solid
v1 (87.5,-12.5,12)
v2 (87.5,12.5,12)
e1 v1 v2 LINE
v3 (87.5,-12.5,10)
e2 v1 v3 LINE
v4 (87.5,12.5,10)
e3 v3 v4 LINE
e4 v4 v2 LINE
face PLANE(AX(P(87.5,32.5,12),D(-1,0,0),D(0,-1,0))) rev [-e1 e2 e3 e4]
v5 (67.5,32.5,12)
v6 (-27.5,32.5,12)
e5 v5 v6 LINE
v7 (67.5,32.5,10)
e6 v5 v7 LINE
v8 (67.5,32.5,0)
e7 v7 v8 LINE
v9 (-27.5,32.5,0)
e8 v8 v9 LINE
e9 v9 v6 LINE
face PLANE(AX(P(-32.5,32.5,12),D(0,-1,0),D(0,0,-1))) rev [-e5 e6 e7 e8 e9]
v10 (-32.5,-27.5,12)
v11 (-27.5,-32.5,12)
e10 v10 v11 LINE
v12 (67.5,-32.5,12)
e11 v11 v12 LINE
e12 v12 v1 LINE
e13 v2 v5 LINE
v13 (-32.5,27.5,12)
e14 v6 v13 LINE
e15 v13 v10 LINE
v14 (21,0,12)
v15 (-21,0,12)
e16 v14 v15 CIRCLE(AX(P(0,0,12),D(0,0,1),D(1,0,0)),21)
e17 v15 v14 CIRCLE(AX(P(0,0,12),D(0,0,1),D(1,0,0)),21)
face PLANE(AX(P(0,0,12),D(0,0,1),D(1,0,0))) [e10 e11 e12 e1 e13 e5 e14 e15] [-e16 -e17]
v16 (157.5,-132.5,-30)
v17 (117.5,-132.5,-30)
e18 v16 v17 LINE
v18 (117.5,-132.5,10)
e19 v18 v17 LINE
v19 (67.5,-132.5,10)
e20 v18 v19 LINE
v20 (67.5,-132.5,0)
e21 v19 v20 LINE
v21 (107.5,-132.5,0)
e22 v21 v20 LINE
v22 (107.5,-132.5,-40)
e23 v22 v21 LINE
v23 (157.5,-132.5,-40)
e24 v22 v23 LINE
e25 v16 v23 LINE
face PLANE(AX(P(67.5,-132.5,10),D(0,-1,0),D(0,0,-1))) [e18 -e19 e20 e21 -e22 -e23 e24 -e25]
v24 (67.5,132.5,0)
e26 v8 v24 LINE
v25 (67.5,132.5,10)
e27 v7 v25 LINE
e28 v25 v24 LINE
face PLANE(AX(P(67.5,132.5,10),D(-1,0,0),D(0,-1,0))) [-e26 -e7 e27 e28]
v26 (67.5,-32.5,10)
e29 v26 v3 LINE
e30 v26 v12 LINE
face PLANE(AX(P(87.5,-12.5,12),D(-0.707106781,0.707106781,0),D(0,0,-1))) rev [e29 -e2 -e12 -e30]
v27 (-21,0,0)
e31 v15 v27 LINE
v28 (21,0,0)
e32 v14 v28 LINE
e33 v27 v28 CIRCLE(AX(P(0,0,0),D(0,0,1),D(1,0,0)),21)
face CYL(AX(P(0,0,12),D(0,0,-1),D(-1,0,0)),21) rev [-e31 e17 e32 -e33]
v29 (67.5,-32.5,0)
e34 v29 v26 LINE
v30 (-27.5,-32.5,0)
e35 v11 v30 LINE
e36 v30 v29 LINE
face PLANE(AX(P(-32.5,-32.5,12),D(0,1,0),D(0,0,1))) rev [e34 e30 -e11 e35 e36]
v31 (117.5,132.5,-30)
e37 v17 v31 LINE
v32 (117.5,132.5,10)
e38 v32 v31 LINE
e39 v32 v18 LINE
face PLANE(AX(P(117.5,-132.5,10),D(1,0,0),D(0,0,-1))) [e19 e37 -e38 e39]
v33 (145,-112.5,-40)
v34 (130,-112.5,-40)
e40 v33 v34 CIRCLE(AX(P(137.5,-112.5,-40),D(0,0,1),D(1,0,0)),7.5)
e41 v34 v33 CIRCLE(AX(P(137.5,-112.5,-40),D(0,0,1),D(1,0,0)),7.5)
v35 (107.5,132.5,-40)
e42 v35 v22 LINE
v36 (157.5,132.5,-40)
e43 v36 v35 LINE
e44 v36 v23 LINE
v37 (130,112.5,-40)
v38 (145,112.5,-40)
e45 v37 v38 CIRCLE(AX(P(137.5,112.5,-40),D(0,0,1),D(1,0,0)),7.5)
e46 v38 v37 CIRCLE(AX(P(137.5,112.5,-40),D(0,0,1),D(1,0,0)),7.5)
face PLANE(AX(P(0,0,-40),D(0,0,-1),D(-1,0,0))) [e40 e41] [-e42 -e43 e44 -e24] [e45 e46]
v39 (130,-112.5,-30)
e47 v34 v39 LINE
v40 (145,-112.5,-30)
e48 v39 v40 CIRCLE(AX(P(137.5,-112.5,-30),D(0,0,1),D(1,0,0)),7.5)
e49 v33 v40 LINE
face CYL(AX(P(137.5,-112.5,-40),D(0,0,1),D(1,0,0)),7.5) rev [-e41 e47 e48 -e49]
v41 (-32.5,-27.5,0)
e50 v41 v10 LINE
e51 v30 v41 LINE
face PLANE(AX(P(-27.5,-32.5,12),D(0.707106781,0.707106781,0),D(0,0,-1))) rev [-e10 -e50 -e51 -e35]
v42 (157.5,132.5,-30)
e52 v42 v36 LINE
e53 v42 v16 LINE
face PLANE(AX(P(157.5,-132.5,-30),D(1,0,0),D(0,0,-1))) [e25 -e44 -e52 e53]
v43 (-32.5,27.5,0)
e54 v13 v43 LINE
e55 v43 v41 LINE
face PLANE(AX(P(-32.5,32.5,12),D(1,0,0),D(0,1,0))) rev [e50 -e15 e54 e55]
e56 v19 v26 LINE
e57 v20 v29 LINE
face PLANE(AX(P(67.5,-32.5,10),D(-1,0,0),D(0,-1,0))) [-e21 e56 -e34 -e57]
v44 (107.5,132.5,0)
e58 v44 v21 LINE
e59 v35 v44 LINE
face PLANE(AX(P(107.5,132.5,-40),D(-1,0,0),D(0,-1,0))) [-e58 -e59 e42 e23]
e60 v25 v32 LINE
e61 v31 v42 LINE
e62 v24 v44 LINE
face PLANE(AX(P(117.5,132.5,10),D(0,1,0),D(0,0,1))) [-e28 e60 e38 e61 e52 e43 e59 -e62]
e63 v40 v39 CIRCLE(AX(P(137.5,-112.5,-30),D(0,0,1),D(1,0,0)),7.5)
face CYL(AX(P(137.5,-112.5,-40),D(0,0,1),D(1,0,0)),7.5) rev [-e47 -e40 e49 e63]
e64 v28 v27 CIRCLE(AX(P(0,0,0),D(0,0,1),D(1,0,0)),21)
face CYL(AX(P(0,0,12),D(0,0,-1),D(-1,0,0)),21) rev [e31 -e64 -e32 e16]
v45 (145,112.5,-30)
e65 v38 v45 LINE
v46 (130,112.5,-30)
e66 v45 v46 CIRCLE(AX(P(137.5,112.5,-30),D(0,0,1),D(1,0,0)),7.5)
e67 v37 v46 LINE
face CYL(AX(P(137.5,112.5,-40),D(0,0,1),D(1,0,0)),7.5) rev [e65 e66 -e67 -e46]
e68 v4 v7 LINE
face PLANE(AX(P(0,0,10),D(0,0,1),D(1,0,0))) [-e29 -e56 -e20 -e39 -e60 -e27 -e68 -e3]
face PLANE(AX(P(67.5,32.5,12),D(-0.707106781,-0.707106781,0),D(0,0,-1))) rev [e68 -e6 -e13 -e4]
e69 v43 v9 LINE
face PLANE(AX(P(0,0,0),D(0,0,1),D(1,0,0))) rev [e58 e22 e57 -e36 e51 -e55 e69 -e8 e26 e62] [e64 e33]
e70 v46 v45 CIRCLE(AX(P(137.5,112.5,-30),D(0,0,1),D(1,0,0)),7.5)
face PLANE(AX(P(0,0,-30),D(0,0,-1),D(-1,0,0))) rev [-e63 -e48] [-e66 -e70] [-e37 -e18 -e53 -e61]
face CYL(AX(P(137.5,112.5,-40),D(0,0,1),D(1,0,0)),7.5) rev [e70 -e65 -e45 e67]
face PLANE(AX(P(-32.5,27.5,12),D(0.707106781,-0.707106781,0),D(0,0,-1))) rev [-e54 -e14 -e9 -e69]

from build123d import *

# Parameters (mm, degrees)
SKETCH_1_R          = 21
EXTRUDE_1_DEPTH     = 12
CHAMFER_1_SIZE      = 5
CHAMFER_2_SIZE      = 20
EXTRUDE_2_DEPTH     = 10
SKETCH_4_W          = 10
SKETCH_4_H          = 265
EXTRUDE_3_DEPTH     = 50
SKETCH_6_W          = 50
SKETCH_6_H          = 265
EXTRUDE_4_DEPTH     = 10
SKETCH_7_R          = 7.5
CUT_EXTRUDE_1_DEPTH = 211.063085762


with BuildPart() as part:
    # 草图1 → 凸台-拉伸1 (new body)
    with BuildSketch(Plane.XY):
        Polygon((32.5, 32.5), (87.5, 32.5), (87.5, -32.5), (32.5, -32.5), (-32.5, -32.5), (-32.5, 32.5), align=None)
        Circle(SKETCH_1_R, mode=Mode.SUBTRACT)
    extrude(amount=EXTRUDE_1_DEPTH)

    # 倒角1
    chamfer_1_edges = [part.edges().sort_by_distance(p)[0] for p in [
        (-32.5, -32.5, 6),
        (-32.5, 32.5, 6),
    ]]
    chamfer(chamfer_1_edges, length=CHAMFER_1_SIZE)

    # 倒角2
    chamfer_2_edges = [part.edges().sort_by_distance(p)[0] for p in [
        (87.5, 32.5, 6),
        (87.5, -32.5, 6),
    ]]
    chamfer(chamfer_2_edges, length=CHAMFER_2_SIZE)

    # 草图3 → 凸台-拉伸2 (add)
    with BuildSketch(Plane(origin=(0, 0, 0), x_dir=(-1, 0, 0), z_dir=(0, 0, -1))):
        Polygon((-67.5, 32.5), (-87.5, 12.5), (-87.5, -12.5), (-67.5, -32.5), (-67.5, -132.5), (-117.5, -132.5), (-117.5, 132.5), (-67.5, 132.5), align=None)
    extrude(amount=-EXTRUDE_2_DEPTH)

    # 草图4 → 凸台-拉伸3 (add)
    with BuildSketch(Plane.XY.offset(10)):
        with Locations((112.5, 0)):
            Rectangle(SKETCH_4_W, SKETCH_4_H)
    extrude(amount=-EXTRUDE_3_DEPTH)

    # 草图6 → 凸台-拉伸4 (add)
    with BuildSketch(Plane(origin=(0, 0, -40), x_dir=(-1, 0, 0), z_dir=(0, 0, -1))):
        with Locations((-132.5, 0)):
            Rectangle(SKETCH_6_W, SKETCH_6_H)
    extrude(amount=-EXTRUDE_4_DEPTH)

    # 草图7 → 切除-拉伸1 (cut, through all)
    with BuildSketch(Plane.XY.offset(-30)):
        with Locations((137.5, 112.5)):
            Circle(SKETCH_7_R)
        with Locations((137.5, -112.5)):
            Circle(SKETCH_7_R)
    extrude(amount=-CUT_EXTRUDE_1_DEPTH, mode=Mode.SUBTRACT)


solid = part.part
